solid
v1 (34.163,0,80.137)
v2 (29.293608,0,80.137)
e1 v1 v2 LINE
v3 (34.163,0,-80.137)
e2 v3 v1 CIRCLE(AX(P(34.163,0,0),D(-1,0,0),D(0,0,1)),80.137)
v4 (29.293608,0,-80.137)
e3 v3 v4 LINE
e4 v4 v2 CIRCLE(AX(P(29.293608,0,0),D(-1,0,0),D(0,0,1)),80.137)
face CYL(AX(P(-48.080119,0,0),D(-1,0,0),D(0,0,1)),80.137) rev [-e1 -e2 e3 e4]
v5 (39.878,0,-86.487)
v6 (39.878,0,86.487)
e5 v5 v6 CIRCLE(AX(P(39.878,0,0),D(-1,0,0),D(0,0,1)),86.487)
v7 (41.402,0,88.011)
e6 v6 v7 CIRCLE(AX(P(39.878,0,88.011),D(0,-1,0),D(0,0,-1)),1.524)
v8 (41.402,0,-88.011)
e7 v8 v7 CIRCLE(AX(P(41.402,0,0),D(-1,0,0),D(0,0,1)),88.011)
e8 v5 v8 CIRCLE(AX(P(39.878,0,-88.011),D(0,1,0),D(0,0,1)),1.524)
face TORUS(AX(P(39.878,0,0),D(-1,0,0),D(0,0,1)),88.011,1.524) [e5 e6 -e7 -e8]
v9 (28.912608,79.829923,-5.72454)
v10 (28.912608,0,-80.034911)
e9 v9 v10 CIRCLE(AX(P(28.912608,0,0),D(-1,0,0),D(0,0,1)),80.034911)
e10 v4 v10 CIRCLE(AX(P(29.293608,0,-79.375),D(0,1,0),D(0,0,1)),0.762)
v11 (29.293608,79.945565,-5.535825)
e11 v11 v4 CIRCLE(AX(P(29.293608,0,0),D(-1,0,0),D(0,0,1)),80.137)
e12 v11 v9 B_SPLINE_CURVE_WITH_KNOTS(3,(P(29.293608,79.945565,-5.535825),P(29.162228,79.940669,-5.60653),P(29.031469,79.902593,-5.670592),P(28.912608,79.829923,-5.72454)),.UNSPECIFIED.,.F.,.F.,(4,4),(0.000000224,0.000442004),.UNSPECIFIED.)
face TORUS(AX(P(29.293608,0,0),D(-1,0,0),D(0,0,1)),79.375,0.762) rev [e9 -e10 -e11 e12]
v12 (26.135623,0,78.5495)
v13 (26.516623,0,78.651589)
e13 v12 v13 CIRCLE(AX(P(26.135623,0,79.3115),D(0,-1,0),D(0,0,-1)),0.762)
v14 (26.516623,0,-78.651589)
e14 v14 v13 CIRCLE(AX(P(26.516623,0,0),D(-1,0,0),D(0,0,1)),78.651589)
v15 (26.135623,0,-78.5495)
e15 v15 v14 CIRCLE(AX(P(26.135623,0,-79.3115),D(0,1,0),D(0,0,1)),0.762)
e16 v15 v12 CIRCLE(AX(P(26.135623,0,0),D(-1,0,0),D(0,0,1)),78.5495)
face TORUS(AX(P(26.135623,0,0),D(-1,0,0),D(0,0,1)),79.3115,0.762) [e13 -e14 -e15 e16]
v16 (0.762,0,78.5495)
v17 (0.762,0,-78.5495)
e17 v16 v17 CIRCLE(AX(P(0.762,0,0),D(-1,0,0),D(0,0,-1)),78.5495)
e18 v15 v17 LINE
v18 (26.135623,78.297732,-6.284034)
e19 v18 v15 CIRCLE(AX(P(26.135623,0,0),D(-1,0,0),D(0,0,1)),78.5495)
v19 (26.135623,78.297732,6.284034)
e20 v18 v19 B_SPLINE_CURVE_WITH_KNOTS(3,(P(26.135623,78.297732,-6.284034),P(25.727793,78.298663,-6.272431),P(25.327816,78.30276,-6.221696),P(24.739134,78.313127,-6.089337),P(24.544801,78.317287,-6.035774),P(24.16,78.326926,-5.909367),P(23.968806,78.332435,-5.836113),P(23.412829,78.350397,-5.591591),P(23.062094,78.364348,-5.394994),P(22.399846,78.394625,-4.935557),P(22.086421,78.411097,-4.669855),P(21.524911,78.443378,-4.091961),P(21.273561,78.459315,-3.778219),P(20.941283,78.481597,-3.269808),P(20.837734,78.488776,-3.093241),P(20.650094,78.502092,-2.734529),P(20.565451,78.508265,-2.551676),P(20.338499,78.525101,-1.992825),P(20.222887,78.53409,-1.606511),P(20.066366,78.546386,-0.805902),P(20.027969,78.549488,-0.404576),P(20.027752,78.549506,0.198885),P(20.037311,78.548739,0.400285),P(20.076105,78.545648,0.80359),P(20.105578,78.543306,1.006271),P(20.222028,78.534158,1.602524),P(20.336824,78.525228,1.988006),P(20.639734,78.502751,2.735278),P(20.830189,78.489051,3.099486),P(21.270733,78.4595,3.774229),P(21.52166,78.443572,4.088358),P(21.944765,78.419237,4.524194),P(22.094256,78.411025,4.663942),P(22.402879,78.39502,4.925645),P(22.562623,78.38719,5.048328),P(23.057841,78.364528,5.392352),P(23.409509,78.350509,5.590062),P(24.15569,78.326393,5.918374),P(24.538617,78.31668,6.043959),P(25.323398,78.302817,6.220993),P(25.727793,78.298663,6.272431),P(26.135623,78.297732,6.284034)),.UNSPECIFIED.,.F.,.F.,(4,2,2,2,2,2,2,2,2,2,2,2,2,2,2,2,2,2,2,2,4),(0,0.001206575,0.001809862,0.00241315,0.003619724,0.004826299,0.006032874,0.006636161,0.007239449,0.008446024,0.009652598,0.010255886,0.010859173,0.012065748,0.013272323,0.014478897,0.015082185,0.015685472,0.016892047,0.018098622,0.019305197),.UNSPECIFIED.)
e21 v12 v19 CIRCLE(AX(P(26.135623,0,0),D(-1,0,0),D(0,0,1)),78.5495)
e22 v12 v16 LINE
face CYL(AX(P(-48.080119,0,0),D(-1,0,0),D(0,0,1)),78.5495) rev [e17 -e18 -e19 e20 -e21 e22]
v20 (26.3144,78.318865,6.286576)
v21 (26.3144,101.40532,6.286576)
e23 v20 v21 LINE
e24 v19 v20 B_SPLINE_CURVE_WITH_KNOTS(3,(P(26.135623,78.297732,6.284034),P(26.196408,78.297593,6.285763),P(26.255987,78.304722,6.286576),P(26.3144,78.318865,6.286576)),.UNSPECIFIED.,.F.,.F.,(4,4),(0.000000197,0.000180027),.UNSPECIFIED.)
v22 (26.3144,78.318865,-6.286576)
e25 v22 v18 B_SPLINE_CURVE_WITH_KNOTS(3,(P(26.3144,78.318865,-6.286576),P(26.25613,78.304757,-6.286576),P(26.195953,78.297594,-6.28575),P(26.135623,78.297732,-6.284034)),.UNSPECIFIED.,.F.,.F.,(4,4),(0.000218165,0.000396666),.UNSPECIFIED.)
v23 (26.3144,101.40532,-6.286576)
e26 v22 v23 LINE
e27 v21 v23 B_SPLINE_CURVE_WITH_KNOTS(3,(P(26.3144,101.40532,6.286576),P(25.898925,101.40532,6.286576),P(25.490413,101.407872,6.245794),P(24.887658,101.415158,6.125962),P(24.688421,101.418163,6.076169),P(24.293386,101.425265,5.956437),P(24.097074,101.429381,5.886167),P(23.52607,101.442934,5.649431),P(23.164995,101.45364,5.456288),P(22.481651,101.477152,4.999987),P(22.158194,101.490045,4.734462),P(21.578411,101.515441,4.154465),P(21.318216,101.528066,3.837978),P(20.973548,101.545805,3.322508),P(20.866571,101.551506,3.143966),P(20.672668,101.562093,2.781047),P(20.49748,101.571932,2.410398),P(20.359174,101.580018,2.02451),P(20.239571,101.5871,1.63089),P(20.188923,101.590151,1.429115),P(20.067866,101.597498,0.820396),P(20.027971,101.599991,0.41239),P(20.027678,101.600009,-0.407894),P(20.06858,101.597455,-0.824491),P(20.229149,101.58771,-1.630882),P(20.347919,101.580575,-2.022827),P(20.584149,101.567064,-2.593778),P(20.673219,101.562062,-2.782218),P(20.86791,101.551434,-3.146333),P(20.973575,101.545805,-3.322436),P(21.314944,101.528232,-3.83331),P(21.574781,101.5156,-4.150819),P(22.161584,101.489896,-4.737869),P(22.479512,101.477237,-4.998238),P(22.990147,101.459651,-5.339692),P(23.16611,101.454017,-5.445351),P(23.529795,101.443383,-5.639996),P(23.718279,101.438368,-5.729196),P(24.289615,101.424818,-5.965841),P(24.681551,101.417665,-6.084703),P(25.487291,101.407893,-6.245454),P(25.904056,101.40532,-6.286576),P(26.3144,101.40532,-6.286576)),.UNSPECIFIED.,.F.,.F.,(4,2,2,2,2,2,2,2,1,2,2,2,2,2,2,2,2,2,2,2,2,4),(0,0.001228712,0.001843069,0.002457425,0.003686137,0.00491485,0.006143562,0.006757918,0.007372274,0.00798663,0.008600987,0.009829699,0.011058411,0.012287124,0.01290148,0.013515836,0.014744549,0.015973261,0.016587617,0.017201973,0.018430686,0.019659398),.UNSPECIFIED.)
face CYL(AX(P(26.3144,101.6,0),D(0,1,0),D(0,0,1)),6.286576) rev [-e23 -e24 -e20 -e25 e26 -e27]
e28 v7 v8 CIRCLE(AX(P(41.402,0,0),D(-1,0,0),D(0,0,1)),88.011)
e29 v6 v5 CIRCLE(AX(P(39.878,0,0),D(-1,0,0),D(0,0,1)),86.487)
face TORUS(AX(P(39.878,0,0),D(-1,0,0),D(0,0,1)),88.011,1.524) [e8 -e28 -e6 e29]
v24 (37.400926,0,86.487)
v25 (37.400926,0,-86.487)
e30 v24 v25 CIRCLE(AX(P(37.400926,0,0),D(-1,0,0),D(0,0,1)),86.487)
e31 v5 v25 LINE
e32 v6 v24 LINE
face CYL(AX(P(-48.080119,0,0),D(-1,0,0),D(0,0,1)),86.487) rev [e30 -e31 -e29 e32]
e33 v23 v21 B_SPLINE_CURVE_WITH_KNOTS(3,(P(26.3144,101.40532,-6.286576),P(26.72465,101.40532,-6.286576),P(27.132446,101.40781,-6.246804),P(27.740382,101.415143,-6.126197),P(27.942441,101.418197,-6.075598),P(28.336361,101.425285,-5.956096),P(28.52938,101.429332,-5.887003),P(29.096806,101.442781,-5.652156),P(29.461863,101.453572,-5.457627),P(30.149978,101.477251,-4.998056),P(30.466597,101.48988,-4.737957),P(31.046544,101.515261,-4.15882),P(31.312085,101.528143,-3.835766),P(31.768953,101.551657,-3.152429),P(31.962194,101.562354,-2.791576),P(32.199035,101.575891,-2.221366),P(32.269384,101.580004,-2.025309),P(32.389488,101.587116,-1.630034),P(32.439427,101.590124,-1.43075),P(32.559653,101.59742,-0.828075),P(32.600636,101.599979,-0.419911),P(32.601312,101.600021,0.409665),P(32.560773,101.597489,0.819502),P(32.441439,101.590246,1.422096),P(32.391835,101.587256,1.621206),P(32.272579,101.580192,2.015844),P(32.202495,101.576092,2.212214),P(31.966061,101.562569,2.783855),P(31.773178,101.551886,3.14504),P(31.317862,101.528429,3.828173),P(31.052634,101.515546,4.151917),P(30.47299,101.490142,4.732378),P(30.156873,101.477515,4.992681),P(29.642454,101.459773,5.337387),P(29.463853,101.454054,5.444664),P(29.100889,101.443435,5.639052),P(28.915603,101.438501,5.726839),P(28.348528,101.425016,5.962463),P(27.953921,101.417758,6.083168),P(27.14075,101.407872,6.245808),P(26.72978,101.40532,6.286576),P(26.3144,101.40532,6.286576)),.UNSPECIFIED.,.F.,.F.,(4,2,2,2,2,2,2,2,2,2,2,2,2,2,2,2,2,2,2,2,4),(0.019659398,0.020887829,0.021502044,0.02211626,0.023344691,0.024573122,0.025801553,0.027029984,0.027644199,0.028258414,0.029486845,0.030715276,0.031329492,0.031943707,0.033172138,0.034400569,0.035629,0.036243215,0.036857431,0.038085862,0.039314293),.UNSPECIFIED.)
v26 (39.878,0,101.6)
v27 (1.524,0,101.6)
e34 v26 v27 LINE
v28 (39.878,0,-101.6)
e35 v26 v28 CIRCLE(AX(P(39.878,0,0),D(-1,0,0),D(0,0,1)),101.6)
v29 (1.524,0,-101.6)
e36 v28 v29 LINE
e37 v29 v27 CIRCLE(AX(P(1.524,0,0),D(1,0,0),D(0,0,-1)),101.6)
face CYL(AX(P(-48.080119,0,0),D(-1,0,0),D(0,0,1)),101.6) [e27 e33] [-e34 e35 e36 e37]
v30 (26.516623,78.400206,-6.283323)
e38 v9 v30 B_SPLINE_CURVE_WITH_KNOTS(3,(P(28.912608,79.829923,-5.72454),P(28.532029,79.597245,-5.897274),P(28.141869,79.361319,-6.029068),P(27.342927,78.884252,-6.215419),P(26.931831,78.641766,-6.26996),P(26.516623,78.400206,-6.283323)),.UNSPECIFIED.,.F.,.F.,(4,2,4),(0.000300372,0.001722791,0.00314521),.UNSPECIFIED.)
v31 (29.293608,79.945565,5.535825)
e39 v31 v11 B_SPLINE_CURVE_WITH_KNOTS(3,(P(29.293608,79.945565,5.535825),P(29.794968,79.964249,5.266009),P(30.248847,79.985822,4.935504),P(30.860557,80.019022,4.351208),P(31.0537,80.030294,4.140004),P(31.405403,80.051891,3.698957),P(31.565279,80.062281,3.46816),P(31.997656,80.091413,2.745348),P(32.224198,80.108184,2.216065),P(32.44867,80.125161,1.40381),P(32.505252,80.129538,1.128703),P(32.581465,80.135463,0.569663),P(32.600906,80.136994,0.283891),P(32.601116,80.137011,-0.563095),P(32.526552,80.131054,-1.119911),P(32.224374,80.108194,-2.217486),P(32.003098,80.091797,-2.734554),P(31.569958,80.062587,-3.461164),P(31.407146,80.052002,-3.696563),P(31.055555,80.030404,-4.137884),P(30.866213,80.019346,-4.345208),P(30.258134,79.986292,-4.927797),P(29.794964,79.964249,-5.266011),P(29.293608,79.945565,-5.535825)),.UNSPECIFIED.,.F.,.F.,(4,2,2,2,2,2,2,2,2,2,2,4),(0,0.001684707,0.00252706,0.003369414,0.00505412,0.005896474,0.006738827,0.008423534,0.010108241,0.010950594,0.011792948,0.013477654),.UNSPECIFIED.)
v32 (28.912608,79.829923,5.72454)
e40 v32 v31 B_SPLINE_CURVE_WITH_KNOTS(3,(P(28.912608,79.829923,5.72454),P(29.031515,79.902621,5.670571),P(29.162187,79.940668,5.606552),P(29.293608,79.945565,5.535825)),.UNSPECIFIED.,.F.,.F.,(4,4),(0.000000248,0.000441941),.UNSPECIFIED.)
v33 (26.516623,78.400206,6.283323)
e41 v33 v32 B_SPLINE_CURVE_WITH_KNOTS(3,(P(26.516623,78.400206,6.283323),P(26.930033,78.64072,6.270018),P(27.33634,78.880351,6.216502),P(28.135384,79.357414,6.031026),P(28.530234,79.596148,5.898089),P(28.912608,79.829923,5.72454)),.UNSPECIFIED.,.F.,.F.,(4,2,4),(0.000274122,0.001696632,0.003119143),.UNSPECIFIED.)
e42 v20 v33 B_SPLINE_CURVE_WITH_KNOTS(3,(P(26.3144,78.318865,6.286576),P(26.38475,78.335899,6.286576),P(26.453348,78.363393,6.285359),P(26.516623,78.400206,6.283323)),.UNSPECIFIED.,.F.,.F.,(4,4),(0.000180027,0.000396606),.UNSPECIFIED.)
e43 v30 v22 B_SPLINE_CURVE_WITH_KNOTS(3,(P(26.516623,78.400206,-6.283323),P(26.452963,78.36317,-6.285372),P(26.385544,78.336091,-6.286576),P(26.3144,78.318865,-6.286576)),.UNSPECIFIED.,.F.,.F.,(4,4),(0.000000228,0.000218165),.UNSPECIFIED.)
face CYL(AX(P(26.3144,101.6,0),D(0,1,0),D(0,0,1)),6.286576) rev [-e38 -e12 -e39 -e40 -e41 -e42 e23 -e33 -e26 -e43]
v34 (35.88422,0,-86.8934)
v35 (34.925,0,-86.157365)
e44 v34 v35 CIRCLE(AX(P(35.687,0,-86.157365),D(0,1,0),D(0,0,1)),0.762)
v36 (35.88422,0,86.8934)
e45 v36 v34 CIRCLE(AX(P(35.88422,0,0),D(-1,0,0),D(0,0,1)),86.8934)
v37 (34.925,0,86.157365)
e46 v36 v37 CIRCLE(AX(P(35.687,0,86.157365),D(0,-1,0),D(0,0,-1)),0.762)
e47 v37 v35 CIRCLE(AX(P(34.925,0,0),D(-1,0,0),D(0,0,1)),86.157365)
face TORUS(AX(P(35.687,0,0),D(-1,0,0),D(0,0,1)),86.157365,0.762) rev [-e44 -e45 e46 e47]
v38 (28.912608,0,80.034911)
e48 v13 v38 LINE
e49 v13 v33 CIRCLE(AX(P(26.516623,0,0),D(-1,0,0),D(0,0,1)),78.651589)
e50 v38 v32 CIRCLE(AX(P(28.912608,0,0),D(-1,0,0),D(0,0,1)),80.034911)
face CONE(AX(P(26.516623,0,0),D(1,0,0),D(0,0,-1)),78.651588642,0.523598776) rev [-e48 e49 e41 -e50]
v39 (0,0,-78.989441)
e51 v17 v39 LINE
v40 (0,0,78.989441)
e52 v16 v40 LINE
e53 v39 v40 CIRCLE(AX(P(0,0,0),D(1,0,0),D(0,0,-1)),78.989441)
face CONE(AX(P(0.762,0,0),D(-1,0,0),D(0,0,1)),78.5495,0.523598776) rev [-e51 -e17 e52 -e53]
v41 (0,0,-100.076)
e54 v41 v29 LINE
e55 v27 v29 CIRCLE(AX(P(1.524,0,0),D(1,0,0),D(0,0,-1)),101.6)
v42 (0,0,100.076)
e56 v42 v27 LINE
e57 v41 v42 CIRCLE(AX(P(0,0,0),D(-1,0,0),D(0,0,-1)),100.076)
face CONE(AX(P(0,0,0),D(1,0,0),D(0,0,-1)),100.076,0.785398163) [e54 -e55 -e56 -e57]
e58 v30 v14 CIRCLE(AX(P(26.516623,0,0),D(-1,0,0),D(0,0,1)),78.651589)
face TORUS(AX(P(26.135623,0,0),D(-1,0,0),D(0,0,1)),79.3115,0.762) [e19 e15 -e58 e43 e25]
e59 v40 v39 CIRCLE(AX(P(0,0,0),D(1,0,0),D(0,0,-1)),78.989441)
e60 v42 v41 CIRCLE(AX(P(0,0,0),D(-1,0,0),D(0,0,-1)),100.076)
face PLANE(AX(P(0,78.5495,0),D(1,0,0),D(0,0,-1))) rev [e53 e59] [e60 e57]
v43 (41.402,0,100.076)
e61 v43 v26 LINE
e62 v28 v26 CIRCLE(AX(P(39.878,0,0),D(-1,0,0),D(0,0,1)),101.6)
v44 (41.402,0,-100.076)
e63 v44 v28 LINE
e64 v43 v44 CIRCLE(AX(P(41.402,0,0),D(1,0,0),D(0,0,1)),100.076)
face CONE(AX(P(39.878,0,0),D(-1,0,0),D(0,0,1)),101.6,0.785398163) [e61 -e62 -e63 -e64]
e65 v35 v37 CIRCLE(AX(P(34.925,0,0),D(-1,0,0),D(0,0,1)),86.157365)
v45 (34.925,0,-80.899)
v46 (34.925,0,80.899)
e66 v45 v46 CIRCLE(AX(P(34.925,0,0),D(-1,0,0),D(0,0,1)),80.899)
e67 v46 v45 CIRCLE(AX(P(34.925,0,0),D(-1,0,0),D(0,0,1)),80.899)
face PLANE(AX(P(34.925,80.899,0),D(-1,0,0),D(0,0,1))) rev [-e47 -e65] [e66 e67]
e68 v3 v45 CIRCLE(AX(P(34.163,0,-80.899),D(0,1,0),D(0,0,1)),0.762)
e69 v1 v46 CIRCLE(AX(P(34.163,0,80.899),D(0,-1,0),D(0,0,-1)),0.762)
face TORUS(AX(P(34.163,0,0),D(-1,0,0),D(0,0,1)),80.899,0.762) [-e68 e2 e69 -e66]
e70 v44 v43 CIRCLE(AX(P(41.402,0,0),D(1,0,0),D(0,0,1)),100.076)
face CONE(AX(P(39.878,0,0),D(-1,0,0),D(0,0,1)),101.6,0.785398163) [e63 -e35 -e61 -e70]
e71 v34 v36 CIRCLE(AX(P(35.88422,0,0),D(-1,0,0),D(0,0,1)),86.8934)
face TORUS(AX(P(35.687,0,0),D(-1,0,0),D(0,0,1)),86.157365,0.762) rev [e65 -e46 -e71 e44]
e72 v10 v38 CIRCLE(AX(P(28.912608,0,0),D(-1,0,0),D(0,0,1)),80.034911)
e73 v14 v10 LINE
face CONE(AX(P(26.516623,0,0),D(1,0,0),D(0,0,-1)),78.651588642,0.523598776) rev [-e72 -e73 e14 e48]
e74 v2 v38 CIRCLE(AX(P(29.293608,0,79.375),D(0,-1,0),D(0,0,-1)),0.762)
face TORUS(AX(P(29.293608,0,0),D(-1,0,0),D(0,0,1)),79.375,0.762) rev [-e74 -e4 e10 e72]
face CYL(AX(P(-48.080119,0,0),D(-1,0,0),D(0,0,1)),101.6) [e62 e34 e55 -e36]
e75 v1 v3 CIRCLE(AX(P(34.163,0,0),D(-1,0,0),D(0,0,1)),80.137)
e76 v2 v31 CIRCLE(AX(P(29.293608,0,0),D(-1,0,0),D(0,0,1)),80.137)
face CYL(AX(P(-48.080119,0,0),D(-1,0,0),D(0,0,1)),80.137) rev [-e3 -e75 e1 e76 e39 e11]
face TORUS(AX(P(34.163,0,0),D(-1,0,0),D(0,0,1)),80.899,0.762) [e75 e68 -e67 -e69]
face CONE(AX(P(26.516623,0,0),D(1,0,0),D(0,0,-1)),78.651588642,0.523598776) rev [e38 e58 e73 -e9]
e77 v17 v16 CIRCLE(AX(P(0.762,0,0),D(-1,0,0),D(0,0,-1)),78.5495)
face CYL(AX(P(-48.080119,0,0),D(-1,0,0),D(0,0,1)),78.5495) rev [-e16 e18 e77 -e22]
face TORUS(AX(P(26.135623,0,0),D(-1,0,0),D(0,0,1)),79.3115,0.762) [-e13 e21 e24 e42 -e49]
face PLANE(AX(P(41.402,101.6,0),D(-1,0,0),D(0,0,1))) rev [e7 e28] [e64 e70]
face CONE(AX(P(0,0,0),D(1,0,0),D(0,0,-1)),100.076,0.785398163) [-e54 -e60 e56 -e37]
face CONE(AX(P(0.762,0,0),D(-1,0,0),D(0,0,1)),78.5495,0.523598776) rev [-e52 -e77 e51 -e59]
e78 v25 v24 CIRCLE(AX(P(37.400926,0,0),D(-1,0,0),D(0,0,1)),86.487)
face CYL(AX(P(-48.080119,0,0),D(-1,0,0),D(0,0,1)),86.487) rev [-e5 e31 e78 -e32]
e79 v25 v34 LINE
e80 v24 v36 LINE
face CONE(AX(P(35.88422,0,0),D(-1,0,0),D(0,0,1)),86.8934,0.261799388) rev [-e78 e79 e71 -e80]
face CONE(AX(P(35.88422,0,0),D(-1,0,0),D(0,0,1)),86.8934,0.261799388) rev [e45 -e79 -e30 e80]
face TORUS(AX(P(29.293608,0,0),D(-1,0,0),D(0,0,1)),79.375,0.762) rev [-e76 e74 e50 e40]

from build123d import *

# Parameters (mm, degrees)
CHAMFER2_SIZE                      = 0.762
CHAMFER2_SIZE2                     = 0.439940905
CHAMFER3_SIZE                      = 1.524
F_1_8_NPT_TAPPED_HOLE1_D           = 8.4328
F_1_8_NPT_TAPPED_HOLE1_DEPTH       = 63.119
F_1_8_NPT_TAPPED_HOLE1_CBORE_D     = 12.5731524
F_1_8_NPT_TAPPED_HOLE1_CBORE_DEPTH = 58.42
F_1_8_NPT_TAPPED_HOLE1_TIP         = 2.533468714


with BuildPart() as part:
    # Sketch1 → Revolve1 (revolve)
    with BuildSketch(Plane.XY, mode=Mode.PRIVATE) as revolve1_sk:
        with BuildLine():
            Line((0, 101.6), (41.402, 101.6))
            Line((41.402, 101.6), (41.402, 88.011))
            ThreePointArc((41.402, 88.011), (40.955630735, 86.933369265), (39.878, 86.487))
            Line((39.878, 86.487), (37.400925561, 86.487))
            Line((37.400925561, 86.487), (35.884220112, 86.8934))
            ThreePointArc((35.884220112, 86.8934), (35.223123791, 86.761899766), (34.925, 86.15736452))
            Line((34.925, 86.15736452), (34.925, 80.899))
            ThreePointArc((34.925, 80.899), (34.701815367, 80.360184633), (34.163, 80.137))
            Line((34.163, 80.137), (29.293607942, 80.137))
            ThreePointArc((29.293607942, 80.137), (29.096387829, 80.11103548), (28.912607942, 80.034911358))
            Line((28.912607942, 80.034911358), (26.516622715, 78.651588642))
            ThreePointArc((26.516622715, 78.651588642), (26.332842828, 78.57546452), (26.135622715, 78.5495))
            Line((26.135622715, 78.5495), (0, 78.5495))
            Line((0, 78.5495), (0, 101.6))
        make_face()
    revolve(revolve1_sk.sketch.rotate(Axis((-48.080119454, 0, 0), (1, 0, 0)), 90), axis=Axis((-48.080119454, 0, 0), (1, 0, 0)))

    # Chamfer2
    chamfer2_edges = [part.edges().sort_by_distance(p)[0] for p in [
        (0, 0, -78.5495),
    ]]
    chamfer2_side = [part.faces().sort_by_distance(p)[0] for p in [
        (13.067811358, 0, -78.5495),
    ]]
    chamfer(chamfer2_edges, length=CHAMFER2_SIZE, length2=CHAMFER2_SIZE2, reference=chamfer2_side[0])

    # Chamfer3
    chamfer3_edges = [part.edges().sort_by_distance(p)[0] for p in [
        (41.402, 0, -101.6),
        (0, 0, -101.6),
    ]]
    chamfer(chamfer3_edges, length=CHAMFER3_SIZE)

    # 1/8 NPT Tapped Hole1
    with Locations(Plane(origin=(26.3144, 101.6, 0), x_dir=(0, 0, 1), z_dir=(0, 1, 0))):
        with Locations((0, 0)):
            CounterBoreHole(F_1_8_NPT_TAPPED_HOLE1_D / 2, F_1_8_NPT_TAPPED_HOLE1_CBORE_D / 2, F_1_8_NPT_TAPPED_HOLE1_CBORE_DEPTH, depth=F_1_8_NPT_TAPPED_HOLE1_DEPTH)
            with Locations((0, 0, -(F_1_8_NPT_TAPPED_HOLE1_DEPTH + F_1_8_NPT_TAPPED_HOLE1_TIP / 2))):  # 118° drill point
                Cone(0, F_1_8_NPT_TAPPED_HOLE1_D / 2, F_1_8_NPT_TAPPED_HOLE1_TIP, mode=Mode.SUBTRACT)


solid = part.part
